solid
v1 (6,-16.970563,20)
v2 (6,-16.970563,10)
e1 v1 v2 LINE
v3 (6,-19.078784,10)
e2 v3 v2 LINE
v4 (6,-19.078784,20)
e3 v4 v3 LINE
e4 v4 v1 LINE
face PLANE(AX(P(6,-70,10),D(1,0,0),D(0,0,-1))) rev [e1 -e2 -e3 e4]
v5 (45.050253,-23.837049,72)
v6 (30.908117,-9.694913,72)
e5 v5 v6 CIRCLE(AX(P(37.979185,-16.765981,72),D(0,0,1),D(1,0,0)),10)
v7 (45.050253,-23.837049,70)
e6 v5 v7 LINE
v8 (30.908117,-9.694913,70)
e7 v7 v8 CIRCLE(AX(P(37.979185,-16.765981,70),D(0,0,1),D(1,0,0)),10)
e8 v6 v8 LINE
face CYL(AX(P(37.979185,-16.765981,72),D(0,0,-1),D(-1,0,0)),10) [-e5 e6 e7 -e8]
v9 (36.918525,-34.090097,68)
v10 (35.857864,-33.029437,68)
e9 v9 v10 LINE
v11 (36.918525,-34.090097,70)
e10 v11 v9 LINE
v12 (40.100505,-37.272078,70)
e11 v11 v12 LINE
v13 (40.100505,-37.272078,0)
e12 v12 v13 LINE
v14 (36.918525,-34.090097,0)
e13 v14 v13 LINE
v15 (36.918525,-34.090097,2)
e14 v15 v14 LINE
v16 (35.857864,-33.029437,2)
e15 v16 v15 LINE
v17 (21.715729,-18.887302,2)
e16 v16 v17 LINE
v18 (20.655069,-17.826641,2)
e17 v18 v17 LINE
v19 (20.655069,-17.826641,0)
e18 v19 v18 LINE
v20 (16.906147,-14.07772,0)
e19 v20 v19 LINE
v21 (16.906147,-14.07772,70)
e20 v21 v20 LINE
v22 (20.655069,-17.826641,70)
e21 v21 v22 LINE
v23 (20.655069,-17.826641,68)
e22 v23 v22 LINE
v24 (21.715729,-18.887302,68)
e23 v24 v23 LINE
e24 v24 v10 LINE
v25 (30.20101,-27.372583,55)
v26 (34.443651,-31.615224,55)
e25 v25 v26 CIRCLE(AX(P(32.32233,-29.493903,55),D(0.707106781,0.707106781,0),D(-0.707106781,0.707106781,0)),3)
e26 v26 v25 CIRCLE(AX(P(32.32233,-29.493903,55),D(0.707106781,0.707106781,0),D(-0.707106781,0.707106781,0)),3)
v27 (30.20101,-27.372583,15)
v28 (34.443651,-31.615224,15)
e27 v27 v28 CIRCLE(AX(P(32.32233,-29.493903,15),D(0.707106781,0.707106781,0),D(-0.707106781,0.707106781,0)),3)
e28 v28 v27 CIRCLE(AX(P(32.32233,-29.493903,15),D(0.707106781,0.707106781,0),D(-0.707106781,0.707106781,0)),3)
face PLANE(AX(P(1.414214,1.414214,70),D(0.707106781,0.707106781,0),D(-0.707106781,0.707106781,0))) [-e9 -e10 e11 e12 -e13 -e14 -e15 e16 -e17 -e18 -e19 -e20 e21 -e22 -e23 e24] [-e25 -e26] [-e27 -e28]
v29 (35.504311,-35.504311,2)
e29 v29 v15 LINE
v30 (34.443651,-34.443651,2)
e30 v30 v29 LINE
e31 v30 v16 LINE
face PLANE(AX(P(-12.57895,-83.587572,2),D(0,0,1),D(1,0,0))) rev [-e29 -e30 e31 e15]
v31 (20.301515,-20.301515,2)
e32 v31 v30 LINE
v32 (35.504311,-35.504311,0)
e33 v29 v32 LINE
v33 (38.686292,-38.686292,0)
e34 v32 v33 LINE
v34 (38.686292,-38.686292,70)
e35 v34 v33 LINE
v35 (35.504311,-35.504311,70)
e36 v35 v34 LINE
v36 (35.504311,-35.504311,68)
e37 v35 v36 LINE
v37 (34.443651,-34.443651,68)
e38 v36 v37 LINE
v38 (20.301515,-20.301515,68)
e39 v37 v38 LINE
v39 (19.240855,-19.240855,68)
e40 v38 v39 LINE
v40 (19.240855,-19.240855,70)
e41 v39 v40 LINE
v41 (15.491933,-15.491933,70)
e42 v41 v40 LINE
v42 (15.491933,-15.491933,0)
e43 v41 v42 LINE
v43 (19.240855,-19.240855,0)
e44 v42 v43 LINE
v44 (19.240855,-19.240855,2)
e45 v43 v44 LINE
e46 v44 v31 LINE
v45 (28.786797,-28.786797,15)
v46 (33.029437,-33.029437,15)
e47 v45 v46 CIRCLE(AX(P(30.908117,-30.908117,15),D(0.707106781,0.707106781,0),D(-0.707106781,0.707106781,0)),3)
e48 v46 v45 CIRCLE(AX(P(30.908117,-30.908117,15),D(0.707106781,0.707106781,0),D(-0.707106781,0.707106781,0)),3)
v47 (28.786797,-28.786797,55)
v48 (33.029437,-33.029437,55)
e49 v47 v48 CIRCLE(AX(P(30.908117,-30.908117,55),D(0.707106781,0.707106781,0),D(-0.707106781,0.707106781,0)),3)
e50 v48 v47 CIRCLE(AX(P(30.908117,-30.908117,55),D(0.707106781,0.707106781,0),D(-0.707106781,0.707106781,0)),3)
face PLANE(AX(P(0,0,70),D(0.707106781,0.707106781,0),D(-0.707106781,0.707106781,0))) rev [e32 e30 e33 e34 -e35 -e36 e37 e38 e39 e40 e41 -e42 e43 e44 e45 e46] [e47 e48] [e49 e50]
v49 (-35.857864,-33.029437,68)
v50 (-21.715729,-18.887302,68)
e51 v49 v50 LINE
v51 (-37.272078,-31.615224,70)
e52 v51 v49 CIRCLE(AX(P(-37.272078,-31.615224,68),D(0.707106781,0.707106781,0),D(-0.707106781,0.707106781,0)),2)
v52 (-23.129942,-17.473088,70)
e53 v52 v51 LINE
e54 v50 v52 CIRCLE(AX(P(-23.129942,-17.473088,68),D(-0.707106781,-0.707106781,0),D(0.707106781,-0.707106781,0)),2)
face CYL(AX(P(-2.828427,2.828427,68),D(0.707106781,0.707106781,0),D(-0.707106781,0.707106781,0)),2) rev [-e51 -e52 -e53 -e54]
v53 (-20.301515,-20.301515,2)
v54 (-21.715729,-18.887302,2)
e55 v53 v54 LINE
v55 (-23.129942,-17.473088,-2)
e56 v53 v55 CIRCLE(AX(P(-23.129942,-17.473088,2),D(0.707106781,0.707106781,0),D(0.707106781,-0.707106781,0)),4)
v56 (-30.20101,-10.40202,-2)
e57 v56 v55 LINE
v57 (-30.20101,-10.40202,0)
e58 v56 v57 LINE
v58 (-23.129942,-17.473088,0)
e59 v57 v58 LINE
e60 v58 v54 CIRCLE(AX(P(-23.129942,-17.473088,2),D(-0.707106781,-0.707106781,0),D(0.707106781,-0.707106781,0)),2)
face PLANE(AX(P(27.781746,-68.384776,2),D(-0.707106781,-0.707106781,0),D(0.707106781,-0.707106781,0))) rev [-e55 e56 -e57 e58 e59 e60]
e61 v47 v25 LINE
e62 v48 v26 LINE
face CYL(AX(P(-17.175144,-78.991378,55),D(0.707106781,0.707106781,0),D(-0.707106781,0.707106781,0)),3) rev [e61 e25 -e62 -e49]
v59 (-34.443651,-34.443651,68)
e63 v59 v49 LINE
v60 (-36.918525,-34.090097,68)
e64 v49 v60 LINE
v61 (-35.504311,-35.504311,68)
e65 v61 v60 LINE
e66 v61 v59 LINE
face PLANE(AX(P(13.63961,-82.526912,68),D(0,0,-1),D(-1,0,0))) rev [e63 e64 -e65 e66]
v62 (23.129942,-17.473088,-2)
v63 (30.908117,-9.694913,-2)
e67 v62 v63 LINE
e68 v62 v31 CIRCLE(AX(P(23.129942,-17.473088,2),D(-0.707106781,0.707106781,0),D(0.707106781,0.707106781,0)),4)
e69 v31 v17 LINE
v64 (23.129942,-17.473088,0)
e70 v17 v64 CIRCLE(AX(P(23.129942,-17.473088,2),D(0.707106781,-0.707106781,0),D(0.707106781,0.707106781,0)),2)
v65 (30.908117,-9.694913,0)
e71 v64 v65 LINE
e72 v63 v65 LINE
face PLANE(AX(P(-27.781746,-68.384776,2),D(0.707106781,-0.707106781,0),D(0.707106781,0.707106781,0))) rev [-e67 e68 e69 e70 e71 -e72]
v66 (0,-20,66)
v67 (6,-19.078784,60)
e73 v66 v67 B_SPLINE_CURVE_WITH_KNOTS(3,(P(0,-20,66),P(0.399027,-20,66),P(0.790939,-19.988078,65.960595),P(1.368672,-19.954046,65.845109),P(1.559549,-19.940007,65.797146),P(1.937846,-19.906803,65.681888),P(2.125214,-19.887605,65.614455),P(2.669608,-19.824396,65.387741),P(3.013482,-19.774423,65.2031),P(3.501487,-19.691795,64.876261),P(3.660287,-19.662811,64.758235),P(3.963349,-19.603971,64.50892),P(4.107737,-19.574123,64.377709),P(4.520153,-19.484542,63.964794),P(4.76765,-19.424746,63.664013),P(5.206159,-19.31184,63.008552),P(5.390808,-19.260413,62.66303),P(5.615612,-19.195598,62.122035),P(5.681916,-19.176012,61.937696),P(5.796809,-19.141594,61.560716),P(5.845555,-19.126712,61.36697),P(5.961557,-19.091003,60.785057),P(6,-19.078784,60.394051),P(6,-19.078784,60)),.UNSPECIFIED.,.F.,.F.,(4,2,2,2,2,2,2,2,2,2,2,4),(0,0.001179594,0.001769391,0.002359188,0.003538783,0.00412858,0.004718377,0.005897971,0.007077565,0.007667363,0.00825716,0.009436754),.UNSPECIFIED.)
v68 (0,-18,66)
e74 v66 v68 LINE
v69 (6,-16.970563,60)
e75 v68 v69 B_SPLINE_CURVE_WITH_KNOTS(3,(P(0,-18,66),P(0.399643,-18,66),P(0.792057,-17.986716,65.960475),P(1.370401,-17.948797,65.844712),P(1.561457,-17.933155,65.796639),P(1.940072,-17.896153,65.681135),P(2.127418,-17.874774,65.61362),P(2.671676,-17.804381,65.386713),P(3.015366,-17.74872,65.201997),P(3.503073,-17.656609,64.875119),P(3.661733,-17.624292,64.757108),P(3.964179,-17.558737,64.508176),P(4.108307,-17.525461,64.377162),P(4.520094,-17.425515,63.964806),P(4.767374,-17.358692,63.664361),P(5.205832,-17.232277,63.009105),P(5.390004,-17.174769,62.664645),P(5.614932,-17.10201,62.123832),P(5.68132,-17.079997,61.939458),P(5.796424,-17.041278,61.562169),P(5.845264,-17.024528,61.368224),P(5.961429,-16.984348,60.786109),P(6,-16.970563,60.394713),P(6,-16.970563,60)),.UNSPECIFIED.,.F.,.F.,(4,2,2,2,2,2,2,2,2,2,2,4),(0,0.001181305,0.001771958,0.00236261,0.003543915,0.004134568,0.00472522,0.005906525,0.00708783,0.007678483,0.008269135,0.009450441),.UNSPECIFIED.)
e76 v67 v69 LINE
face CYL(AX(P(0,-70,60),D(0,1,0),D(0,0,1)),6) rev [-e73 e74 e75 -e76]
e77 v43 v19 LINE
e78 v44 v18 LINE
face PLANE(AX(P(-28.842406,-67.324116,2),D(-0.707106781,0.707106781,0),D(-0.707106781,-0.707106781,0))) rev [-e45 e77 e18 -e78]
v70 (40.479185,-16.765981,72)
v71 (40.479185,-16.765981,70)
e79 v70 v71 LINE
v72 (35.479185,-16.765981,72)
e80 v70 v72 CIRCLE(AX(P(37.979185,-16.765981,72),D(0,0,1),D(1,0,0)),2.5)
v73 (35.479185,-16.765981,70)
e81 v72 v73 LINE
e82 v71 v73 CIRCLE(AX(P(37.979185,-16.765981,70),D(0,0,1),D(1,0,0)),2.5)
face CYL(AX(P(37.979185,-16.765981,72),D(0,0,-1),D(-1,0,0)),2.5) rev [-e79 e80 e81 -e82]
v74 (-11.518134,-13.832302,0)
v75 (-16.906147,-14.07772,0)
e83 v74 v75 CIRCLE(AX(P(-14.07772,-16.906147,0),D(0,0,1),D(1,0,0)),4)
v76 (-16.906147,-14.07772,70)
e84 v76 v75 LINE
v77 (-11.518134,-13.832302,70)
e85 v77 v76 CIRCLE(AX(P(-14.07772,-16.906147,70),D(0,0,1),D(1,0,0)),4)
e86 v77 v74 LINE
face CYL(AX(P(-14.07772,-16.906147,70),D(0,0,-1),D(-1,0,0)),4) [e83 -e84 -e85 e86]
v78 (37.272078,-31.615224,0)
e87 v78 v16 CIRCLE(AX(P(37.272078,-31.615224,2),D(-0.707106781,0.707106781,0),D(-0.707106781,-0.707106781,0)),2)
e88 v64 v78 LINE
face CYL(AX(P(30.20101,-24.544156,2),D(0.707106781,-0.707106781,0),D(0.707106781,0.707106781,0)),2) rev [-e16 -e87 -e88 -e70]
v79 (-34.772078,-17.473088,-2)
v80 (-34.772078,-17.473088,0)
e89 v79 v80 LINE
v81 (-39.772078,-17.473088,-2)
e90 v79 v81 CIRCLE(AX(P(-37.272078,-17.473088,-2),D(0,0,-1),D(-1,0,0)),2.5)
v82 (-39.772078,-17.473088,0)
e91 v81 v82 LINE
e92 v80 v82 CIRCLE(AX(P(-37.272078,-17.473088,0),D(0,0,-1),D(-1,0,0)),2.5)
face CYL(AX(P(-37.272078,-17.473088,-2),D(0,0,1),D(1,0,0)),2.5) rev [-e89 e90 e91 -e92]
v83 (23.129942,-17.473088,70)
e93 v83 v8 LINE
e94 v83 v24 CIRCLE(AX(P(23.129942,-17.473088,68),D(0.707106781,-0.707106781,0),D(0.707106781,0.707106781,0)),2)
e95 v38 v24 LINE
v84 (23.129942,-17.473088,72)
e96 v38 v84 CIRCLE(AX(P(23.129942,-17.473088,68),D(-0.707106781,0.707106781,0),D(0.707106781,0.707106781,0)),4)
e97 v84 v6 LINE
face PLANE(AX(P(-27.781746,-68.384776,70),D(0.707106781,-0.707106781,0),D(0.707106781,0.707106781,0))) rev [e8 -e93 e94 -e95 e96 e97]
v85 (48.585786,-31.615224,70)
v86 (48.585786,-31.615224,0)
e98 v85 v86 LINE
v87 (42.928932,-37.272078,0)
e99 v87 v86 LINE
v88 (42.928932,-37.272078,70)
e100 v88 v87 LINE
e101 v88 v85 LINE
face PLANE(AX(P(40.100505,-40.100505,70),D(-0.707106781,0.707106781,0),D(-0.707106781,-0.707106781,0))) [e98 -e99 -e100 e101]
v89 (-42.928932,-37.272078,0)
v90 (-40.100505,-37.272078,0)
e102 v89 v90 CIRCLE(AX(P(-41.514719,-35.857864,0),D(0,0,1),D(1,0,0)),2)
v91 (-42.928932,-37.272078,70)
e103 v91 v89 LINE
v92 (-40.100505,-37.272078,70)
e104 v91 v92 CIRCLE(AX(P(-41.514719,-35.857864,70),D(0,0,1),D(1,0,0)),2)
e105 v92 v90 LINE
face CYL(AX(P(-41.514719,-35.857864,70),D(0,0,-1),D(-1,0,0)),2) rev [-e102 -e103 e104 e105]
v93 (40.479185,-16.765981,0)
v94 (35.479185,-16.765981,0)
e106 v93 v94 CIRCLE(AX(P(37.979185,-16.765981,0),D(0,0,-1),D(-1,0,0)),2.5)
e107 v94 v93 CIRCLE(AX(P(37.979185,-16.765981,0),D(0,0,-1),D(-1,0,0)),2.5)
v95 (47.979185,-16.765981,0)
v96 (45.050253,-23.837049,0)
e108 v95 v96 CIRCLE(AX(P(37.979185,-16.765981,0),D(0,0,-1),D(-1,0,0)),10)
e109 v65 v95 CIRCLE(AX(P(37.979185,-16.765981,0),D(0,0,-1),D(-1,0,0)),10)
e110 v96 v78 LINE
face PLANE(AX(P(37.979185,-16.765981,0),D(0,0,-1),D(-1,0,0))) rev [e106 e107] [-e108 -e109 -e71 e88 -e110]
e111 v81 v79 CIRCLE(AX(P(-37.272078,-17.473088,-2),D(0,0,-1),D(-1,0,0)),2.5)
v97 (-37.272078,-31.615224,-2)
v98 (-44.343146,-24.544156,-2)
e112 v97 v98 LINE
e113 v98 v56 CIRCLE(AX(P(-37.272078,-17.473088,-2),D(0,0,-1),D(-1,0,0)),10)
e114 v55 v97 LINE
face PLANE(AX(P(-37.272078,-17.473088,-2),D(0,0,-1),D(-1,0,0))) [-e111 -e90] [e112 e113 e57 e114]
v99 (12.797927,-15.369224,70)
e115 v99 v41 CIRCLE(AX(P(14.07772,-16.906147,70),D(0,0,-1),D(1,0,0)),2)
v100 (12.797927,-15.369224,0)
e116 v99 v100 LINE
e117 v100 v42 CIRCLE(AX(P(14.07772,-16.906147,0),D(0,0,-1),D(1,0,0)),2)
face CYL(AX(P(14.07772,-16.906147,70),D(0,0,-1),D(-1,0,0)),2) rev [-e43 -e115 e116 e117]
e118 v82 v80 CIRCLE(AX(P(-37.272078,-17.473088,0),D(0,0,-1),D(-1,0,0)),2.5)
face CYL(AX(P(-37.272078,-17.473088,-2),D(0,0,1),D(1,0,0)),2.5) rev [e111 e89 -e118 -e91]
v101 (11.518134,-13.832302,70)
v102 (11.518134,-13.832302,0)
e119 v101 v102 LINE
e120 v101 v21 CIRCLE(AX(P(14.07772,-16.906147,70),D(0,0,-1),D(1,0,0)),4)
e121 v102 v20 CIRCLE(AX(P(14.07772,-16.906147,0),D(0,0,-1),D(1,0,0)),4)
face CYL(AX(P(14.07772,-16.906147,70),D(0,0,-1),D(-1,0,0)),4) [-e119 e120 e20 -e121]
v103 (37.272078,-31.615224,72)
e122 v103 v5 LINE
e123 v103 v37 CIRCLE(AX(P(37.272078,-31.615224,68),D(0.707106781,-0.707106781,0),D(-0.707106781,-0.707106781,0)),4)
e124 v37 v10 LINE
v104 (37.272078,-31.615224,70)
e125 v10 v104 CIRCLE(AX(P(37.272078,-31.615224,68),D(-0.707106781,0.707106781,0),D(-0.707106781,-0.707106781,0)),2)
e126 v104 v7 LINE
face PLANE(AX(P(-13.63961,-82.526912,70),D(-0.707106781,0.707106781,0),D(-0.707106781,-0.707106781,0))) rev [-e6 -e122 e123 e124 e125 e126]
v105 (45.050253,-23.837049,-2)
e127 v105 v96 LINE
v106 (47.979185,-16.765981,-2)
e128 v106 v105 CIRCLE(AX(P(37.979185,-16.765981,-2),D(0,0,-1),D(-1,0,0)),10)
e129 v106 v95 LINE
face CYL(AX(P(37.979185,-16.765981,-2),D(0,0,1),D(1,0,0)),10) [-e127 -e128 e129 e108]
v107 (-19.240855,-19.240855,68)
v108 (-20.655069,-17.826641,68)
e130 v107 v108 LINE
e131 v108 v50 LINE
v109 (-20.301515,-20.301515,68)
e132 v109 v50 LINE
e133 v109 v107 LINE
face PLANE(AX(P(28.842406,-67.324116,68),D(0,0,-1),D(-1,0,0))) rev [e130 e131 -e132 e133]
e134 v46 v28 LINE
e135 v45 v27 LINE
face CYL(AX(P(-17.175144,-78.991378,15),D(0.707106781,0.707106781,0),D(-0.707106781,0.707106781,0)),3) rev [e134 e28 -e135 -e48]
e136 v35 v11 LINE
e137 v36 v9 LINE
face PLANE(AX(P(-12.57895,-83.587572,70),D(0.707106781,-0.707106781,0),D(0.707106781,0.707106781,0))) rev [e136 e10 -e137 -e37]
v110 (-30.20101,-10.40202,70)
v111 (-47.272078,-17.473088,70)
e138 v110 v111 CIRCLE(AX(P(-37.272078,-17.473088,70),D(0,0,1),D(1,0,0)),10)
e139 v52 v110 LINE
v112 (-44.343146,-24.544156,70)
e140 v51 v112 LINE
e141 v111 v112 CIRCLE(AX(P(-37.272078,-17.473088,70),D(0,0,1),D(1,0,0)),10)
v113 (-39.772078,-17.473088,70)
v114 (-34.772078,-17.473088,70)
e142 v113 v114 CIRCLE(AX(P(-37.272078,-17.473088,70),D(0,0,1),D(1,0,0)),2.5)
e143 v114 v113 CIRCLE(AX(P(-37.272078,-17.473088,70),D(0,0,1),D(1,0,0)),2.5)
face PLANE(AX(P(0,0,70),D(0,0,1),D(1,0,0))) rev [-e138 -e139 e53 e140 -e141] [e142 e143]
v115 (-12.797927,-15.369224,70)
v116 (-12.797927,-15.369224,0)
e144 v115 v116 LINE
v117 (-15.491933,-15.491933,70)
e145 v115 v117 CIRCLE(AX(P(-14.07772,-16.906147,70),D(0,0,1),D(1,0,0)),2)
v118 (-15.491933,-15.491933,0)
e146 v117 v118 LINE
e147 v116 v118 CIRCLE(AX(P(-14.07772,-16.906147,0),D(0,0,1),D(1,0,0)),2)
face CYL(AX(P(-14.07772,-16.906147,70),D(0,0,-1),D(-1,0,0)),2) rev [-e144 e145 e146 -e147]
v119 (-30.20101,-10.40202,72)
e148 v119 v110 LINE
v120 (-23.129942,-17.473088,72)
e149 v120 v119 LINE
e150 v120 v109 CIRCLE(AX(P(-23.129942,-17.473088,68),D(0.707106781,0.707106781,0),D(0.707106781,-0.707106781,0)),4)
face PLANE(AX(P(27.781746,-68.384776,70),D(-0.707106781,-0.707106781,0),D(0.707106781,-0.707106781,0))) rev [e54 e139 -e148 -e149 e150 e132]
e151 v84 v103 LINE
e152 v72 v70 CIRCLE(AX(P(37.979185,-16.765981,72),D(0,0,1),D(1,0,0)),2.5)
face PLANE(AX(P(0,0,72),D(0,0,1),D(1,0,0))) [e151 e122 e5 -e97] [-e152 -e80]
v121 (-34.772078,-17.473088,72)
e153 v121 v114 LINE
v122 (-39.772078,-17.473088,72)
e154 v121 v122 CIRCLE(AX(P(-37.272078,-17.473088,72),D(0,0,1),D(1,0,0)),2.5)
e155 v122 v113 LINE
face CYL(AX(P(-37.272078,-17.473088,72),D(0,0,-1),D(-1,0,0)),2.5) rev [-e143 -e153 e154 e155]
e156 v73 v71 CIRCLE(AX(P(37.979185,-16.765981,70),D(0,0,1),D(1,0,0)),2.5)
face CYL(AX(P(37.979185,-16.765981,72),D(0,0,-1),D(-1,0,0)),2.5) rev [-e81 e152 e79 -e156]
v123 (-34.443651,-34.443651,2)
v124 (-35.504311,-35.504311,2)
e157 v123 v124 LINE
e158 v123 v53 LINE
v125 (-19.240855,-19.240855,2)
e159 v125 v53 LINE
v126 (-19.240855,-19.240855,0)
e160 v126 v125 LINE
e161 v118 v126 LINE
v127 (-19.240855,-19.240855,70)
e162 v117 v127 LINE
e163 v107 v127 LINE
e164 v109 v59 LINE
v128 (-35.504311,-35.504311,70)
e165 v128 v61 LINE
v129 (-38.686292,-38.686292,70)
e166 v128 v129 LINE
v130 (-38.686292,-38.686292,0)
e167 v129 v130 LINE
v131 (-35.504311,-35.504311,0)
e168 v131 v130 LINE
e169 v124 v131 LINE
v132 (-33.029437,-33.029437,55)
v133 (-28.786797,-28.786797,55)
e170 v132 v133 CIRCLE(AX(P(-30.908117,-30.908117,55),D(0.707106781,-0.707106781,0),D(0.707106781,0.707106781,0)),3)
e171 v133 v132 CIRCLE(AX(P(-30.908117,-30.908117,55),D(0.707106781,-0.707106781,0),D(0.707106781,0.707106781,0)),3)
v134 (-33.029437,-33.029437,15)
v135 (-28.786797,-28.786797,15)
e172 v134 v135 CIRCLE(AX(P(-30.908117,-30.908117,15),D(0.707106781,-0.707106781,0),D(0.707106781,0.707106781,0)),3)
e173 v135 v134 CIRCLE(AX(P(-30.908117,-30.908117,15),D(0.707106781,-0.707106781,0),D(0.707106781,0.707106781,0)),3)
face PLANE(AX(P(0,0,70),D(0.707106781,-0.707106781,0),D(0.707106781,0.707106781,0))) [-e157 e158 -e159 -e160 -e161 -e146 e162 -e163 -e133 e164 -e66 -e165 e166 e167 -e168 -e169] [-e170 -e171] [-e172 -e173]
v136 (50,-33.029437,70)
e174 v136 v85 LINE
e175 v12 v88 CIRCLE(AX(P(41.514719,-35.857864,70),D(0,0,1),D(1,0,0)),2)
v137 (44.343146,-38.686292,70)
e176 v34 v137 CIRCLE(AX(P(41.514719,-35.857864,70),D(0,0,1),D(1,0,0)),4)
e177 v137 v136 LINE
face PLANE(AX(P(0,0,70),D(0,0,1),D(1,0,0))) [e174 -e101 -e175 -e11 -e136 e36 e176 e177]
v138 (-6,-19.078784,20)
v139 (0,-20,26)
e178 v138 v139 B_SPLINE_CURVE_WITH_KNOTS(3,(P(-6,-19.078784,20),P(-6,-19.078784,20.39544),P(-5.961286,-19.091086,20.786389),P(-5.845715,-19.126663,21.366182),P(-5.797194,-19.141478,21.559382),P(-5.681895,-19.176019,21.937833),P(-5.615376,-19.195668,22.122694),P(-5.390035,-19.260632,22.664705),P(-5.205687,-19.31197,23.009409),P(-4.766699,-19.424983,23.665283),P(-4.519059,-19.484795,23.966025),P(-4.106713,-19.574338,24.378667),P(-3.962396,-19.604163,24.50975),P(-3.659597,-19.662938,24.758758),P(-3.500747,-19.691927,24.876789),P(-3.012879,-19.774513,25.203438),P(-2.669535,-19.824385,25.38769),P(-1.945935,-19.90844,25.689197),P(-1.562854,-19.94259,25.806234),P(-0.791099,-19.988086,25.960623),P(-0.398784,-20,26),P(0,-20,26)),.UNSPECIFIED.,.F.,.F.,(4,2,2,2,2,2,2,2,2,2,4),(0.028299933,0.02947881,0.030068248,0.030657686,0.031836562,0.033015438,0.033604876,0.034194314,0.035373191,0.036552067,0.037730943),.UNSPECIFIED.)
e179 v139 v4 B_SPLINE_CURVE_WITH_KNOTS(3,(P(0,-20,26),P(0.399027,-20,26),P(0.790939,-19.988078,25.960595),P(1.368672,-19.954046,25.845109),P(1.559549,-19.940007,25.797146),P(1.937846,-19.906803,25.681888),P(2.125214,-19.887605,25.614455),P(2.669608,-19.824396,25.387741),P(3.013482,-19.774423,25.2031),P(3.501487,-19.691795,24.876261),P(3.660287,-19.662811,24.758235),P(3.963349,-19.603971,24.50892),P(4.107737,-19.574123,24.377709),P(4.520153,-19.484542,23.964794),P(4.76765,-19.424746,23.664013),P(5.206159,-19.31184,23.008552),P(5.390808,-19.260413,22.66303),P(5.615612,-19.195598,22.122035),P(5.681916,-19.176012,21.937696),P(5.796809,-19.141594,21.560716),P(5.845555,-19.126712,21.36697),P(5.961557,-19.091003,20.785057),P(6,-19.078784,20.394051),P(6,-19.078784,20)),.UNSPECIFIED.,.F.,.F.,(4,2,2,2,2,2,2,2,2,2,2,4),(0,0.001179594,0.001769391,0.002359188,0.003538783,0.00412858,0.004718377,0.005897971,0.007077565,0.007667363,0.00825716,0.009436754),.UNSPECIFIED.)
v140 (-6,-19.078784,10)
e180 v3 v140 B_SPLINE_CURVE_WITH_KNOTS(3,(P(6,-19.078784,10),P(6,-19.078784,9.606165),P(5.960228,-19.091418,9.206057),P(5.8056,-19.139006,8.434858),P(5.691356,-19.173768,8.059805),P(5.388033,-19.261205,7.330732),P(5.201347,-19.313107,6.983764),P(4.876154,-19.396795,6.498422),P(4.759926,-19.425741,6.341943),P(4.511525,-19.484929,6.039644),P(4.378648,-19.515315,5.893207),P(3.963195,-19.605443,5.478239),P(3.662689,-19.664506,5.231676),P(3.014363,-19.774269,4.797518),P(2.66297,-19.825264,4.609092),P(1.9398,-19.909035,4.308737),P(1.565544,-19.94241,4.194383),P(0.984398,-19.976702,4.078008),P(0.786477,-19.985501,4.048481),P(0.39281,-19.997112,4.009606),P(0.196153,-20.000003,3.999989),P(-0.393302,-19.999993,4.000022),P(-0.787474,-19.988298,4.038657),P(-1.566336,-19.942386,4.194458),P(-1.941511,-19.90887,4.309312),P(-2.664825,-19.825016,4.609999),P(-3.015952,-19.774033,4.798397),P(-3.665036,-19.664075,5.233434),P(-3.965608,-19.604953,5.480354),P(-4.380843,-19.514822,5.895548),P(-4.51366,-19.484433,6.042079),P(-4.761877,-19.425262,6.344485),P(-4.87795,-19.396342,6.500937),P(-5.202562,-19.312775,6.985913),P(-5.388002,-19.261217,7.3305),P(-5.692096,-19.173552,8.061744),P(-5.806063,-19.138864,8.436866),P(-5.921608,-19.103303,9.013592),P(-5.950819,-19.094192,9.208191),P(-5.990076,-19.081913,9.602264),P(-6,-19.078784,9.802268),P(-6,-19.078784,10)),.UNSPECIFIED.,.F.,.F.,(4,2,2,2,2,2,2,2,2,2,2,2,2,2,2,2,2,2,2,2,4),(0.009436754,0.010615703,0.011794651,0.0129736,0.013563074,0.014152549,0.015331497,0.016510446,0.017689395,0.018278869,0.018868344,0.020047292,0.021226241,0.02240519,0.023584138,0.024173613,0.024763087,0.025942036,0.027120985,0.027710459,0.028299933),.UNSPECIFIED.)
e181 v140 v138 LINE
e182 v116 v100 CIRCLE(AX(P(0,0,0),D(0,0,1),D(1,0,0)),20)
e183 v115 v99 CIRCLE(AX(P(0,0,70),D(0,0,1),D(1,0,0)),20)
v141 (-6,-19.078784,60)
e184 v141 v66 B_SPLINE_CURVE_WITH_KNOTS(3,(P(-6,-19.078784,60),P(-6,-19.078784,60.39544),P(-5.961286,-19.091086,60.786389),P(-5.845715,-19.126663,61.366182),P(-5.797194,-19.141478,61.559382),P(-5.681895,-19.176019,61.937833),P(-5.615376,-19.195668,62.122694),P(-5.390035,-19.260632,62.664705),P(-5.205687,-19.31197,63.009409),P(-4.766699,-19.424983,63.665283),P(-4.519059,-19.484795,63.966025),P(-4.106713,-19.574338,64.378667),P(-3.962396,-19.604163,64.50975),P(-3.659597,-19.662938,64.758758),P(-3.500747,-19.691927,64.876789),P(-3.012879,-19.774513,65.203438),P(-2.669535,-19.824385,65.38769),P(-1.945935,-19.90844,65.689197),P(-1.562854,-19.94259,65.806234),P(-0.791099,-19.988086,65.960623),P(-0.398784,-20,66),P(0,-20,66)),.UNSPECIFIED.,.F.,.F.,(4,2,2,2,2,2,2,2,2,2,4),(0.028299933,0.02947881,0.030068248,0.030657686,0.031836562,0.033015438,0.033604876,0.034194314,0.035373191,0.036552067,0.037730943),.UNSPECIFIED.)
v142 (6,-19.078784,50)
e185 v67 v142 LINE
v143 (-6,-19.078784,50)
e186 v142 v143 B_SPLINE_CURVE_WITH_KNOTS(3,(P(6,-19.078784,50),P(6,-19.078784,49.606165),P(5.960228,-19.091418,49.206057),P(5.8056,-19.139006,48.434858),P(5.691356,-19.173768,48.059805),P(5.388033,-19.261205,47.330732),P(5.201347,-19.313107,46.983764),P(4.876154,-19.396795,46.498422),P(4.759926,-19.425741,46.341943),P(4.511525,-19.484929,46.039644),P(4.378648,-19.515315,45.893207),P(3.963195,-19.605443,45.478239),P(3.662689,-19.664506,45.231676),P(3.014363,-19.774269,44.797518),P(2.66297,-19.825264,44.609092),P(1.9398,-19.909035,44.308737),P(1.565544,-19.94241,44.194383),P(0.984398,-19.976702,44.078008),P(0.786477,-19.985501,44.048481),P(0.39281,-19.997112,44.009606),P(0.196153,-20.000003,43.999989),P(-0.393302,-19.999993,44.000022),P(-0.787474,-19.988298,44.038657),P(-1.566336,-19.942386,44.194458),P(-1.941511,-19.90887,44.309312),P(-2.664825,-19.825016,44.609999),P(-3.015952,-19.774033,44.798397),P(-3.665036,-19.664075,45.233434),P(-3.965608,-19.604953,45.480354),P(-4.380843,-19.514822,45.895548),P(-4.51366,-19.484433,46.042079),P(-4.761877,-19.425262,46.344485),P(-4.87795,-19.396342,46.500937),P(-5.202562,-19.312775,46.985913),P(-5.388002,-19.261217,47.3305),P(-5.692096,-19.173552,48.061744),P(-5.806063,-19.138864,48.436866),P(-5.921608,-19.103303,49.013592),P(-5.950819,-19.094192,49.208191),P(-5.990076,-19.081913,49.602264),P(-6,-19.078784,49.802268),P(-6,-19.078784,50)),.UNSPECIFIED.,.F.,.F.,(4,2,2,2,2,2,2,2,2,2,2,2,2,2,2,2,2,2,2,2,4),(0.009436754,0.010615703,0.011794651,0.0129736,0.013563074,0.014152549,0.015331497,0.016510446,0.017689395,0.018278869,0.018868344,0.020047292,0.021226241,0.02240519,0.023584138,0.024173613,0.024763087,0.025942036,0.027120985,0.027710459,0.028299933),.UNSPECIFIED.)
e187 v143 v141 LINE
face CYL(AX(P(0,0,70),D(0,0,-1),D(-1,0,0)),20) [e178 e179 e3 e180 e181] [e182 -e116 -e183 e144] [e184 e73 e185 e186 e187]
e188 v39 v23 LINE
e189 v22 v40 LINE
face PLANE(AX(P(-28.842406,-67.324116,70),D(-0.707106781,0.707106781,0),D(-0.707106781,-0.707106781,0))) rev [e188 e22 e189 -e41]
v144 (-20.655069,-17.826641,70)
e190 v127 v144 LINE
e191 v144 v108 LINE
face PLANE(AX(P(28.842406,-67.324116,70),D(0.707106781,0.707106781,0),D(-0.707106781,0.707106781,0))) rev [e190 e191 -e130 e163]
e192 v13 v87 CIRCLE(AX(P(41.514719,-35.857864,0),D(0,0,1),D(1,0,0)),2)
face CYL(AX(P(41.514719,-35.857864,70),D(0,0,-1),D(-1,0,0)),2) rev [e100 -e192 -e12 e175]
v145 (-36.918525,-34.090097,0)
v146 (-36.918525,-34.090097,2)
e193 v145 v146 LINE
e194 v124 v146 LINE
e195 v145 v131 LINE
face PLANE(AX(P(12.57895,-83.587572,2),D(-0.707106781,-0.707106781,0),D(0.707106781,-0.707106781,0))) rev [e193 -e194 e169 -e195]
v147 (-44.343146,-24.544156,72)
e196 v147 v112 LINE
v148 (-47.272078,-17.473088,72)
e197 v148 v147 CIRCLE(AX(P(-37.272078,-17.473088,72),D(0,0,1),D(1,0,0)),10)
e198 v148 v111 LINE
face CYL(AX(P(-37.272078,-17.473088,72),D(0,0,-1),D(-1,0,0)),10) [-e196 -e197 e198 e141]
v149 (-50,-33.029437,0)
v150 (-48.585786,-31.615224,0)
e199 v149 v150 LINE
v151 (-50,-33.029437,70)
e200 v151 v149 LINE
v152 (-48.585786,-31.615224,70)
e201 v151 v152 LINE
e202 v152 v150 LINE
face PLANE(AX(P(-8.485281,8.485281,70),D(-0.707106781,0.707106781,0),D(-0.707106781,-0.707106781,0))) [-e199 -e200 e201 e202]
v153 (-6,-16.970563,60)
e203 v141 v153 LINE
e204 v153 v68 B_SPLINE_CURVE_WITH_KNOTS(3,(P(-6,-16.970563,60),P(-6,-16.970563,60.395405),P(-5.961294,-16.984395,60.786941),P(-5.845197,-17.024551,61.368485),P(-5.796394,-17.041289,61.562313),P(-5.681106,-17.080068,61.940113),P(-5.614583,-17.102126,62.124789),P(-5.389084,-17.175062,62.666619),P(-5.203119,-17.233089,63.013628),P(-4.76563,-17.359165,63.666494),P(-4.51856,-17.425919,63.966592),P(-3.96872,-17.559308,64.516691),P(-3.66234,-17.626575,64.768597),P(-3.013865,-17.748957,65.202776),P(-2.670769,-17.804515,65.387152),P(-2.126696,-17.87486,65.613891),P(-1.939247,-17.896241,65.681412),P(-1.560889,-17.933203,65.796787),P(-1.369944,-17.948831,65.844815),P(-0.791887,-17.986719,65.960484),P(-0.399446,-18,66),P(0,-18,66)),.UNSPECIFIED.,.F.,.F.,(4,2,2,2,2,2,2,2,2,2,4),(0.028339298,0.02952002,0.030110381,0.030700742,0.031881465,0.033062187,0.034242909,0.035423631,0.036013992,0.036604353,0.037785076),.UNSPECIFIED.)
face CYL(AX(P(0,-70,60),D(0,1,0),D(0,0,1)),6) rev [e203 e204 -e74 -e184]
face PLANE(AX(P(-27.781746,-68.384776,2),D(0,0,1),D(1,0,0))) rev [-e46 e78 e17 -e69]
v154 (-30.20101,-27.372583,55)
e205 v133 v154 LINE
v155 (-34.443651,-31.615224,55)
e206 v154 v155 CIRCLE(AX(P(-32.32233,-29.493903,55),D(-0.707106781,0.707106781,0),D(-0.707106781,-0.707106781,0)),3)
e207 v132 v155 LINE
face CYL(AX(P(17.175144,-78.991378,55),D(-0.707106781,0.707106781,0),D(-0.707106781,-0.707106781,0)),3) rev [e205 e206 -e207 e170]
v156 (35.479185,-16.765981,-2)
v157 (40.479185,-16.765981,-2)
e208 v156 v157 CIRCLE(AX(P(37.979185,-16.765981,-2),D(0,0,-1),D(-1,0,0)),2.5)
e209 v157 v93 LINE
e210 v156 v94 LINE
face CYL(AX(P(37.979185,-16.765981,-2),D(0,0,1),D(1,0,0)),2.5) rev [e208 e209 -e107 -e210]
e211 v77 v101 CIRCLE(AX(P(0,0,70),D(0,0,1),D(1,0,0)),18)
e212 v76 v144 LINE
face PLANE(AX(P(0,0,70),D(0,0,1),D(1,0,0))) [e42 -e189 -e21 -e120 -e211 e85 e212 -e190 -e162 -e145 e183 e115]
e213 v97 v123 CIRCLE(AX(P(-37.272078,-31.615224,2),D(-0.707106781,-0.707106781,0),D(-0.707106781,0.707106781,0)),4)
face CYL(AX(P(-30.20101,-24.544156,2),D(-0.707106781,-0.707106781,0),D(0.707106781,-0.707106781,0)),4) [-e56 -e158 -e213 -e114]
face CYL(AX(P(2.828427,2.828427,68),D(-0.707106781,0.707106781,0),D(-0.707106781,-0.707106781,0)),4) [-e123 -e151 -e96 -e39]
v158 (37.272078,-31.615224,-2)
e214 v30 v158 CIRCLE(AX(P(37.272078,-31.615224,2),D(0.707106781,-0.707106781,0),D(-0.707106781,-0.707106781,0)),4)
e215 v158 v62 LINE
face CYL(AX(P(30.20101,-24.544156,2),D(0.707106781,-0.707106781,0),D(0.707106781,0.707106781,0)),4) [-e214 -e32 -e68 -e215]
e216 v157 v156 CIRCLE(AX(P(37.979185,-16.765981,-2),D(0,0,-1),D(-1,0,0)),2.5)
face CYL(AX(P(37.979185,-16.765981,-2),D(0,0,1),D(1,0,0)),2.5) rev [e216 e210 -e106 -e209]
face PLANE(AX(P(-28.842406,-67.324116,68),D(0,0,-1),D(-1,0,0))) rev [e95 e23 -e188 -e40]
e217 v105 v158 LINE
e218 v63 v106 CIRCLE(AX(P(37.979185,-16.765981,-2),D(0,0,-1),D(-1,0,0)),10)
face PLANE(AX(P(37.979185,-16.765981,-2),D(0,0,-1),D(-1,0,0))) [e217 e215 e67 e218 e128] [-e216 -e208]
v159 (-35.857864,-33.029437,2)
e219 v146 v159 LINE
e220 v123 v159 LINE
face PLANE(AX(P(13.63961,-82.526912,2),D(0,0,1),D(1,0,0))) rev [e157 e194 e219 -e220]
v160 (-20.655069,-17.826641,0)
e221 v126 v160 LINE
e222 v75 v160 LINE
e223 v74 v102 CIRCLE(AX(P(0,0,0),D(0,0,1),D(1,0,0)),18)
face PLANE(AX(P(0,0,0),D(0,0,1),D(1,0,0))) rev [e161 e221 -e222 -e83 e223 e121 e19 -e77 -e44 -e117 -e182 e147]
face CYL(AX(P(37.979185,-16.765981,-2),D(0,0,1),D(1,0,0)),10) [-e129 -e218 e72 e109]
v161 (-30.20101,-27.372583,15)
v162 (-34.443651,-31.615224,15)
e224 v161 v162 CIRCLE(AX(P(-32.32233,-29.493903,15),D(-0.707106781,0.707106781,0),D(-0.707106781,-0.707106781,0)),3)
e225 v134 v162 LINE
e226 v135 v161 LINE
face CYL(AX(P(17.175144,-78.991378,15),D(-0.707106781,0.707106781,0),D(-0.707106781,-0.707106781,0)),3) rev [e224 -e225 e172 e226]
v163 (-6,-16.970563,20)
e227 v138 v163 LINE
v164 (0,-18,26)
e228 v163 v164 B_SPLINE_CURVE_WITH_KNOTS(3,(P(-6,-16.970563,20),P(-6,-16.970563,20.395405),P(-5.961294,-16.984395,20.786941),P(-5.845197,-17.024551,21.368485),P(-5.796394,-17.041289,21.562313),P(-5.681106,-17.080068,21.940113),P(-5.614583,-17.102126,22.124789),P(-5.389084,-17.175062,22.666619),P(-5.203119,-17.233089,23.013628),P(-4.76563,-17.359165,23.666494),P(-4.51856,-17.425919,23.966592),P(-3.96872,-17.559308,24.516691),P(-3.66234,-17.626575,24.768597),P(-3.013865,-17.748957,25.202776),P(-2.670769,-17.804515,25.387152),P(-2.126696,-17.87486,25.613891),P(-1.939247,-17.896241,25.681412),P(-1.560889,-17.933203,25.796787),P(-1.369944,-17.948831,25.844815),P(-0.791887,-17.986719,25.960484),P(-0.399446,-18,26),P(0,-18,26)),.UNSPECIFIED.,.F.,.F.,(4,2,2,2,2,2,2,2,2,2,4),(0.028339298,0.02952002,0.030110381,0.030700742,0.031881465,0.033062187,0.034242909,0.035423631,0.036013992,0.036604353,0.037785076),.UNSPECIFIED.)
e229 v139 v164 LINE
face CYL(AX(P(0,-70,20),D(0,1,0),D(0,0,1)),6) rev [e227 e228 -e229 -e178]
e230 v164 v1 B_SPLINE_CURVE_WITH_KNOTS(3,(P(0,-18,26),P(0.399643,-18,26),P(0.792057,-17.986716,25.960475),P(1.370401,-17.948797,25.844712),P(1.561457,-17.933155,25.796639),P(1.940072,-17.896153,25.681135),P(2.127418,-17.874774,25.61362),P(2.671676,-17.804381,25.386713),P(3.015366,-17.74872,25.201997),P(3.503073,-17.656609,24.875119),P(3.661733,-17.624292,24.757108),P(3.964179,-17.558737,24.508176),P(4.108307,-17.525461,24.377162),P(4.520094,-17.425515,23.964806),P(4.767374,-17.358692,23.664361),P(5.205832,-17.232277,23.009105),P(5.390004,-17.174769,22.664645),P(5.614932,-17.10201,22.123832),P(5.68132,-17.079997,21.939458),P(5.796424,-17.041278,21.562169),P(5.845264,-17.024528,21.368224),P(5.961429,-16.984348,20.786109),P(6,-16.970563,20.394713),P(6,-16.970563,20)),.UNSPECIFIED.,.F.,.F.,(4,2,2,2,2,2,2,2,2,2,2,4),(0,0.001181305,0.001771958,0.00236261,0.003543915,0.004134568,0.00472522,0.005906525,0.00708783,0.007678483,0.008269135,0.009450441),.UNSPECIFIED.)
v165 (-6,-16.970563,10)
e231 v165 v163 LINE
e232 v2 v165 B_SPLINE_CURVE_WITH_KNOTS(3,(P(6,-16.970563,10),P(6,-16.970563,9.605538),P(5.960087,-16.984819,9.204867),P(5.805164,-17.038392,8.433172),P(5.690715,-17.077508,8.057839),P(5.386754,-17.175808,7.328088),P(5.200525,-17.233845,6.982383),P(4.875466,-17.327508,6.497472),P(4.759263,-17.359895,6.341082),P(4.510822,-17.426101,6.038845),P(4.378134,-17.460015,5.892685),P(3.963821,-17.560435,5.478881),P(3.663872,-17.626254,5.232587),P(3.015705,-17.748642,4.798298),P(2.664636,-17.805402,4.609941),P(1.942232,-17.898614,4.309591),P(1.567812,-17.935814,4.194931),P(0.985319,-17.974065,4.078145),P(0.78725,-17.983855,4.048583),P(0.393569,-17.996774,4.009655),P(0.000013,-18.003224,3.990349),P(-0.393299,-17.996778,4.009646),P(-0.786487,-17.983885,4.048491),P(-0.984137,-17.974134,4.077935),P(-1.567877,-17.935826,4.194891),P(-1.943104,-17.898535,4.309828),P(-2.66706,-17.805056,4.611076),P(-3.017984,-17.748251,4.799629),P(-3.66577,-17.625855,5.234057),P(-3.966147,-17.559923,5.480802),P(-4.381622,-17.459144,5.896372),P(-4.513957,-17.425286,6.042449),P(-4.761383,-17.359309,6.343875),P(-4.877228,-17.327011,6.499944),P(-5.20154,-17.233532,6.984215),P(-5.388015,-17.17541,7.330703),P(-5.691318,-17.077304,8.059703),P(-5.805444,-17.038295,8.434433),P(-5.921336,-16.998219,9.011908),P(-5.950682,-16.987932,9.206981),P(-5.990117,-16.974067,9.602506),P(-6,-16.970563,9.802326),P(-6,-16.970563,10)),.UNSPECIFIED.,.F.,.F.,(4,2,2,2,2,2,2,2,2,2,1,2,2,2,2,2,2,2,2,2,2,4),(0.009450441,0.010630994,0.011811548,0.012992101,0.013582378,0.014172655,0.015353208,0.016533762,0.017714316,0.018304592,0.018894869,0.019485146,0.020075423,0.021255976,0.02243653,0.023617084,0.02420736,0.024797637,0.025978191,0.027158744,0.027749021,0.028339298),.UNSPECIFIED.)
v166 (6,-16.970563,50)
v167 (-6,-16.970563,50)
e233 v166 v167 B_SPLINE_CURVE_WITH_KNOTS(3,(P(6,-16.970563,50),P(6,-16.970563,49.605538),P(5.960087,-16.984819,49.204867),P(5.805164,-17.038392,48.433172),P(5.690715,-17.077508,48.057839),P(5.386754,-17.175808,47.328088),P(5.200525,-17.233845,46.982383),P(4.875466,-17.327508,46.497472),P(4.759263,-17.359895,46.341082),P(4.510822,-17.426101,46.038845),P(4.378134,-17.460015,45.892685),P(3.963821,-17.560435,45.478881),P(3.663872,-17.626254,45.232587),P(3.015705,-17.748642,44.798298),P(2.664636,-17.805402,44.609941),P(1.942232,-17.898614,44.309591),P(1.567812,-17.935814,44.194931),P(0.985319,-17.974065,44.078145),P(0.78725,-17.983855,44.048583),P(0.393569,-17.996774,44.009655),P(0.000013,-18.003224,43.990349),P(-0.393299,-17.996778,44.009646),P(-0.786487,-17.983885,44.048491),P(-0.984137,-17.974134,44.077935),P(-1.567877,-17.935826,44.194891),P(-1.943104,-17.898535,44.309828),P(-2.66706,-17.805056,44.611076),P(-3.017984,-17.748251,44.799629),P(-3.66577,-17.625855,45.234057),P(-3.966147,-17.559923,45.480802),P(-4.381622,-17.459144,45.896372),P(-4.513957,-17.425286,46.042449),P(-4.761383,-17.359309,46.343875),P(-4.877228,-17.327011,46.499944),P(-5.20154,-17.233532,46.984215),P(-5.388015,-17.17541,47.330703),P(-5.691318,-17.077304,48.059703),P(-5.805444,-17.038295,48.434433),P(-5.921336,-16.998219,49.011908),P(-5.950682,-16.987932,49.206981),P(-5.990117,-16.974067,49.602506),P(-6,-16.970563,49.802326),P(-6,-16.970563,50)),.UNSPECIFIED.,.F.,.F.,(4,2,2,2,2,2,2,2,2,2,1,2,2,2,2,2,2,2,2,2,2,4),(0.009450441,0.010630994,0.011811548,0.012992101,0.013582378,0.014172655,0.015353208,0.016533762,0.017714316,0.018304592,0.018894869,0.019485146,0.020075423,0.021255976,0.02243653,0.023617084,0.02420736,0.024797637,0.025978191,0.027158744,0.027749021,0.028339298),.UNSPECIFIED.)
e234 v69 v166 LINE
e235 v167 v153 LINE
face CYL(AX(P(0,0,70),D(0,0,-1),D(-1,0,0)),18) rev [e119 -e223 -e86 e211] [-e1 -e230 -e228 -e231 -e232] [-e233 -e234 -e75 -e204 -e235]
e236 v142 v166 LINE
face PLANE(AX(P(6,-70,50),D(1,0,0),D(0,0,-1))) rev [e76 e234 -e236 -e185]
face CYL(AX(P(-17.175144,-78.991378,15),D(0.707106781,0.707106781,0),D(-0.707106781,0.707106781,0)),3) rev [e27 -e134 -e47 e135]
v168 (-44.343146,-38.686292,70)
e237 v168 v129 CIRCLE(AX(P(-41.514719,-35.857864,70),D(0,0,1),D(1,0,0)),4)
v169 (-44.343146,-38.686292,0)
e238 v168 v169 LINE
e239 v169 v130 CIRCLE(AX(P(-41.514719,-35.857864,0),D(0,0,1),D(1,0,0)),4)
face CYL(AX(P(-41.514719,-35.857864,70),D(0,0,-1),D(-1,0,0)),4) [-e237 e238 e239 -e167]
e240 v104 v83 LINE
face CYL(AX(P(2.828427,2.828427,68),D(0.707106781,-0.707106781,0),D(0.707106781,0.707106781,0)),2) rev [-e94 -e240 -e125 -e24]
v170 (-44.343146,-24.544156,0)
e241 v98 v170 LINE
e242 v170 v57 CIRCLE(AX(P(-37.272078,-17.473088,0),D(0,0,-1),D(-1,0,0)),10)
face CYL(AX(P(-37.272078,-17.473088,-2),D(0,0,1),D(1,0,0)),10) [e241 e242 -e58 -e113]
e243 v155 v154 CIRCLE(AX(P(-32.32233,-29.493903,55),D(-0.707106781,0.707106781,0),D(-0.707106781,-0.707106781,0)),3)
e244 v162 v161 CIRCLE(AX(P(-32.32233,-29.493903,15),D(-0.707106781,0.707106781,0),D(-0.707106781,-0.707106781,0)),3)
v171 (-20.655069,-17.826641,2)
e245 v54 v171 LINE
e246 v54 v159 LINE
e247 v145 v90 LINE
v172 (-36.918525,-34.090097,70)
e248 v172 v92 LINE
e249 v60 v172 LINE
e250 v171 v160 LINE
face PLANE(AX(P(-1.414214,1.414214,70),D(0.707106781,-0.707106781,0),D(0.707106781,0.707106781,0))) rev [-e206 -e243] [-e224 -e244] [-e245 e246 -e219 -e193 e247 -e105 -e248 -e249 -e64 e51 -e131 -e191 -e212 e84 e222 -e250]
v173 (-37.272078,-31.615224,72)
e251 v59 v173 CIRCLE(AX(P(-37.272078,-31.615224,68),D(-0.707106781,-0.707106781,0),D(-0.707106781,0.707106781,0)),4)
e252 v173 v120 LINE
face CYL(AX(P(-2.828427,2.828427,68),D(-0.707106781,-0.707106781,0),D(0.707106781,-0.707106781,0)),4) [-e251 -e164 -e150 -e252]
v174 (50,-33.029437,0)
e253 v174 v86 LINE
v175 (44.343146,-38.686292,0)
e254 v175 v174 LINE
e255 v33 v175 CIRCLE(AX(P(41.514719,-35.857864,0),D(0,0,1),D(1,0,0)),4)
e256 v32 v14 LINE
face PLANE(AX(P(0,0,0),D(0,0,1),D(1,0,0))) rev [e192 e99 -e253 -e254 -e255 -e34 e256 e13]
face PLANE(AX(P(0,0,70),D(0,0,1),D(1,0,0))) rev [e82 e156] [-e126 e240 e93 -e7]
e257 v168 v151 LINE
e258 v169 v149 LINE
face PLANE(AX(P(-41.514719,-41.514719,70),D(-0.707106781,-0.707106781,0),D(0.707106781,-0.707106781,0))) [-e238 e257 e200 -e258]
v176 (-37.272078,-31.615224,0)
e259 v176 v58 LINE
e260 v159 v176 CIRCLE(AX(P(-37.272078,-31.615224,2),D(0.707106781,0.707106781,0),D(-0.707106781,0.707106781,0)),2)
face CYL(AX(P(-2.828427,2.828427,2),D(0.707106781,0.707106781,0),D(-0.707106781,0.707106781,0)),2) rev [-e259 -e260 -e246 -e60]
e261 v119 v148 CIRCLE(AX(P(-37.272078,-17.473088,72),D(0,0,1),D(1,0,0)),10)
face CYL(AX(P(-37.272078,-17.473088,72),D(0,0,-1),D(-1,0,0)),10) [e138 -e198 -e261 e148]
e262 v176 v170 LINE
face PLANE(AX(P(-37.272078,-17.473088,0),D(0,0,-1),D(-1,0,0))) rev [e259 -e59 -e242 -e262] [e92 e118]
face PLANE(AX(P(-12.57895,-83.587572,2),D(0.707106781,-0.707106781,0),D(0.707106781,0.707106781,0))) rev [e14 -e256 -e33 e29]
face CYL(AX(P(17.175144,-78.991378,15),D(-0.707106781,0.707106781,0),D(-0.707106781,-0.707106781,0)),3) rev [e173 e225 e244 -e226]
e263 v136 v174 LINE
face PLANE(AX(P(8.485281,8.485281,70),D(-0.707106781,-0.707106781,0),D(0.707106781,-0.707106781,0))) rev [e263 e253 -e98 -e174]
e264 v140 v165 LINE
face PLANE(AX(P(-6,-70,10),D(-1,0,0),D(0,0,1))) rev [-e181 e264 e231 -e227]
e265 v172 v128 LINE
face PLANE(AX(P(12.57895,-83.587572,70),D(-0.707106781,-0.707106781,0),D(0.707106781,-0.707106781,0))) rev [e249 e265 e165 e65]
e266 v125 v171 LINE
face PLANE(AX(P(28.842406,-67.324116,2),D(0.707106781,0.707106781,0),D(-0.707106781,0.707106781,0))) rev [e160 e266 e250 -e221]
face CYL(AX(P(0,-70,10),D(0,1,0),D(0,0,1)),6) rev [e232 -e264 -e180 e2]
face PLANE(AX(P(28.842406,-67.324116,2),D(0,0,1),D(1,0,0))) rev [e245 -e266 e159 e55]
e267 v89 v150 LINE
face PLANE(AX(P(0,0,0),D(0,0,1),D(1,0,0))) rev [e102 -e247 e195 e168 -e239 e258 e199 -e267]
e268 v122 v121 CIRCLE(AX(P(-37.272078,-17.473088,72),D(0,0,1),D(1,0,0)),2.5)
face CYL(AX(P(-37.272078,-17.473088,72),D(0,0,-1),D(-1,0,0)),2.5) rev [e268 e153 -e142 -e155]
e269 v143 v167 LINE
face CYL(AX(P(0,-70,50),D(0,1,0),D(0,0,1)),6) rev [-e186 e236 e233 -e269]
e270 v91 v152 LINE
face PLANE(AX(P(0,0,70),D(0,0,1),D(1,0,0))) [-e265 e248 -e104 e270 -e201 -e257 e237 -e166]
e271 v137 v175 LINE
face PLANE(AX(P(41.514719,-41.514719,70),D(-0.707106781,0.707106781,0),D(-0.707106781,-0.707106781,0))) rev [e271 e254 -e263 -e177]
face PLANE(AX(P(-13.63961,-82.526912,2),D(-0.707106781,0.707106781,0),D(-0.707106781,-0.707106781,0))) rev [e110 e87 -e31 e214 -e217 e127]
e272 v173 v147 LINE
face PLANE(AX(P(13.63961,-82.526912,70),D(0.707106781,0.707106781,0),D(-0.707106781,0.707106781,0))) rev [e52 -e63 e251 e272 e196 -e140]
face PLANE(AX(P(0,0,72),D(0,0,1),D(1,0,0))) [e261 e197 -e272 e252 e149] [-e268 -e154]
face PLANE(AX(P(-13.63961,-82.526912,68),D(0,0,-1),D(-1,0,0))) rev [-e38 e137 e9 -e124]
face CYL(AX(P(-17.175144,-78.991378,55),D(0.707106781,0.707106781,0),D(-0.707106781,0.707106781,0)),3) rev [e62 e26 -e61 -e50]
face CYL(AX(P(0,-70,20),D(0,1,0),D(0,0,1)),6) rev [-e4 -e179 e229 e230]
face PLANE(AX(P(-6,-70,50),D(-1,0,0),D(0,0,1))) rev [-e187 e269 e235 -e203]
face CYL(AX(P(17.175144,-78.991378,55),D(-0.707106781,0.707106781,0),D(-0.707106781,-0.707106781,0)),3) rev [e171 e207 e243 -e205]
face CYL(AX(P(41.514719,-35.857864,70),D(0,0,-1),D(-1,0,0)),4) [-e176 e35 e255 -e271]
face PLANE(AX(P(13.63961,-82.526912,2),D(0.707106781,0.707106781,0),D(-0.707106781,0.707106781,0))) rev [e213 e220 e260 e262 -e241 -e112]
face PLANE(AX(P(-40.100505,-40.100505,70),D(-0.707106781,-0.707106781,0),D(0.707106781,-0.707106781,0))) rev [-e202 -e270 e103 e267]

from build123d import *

# Parameters (mm, degrees)
SADDLE_BODY_70MM_DEPTH     = 70
FLANGE_NOTCHES_DEPTH       = 70
FLANGE_HOLES_A_SKETCH_R    = 3.0000000000000018
FLANGE_HOLES_A_SKETCH_R_2  = 3
FLANGE_HOLES_A_6_DEPTH     = 70
FLANGE_HOLES_B_SKETCH_R    = 3.0000000000000018
FLANGE_HOLES_B_6_DEPTH     = 70
SADDLE_SLOT_A_SKETCH_W     = 2
SADDLE_SLOT_A_SKETCH_H     = 1.5
SADDLE_SLOT_A_DEPTH        = 70
SADDLE_SLOT_B_SKETCH_W     = 2
SADDLE_SLOT_B_SKETCH_H     = 1.5
SADDLE_SLOT_B_DEPTH        = 70
MOUNTING_EARS_A_SKETCH_R   = 10.000000000000002
MOUNTING_EARS_A_SKETCH_R_2 = 2.5000000000000027
MOUNTING_EARS_A_SKETCH_R_3 = 9.999999999999508
MOUNTING_EARS_A_DEPTH      = 2
MOUNTING_START             = 2
MOUNTING_EARS_B_SKETCH_R   = 2.5000000000000027
MOUNTING_EARS_B_DEPTH      = 2
EAR_FILLETS_R4_R           = 4
EAR_ROOT_FILLETS_R2_R      = 2


with BuildPart() as part:
    # Saddle Profile Sketch → Saddle Body 70mm (new body)
    with BuildSketch(Plane.XY):
        with BuildLine():
            ThreePointArc((-42.928932188134524, -37.27207793864201), (-41.51471862576144, -37.85786437626892), (-40.100505063388304, -37.27207793864207))
            Line((-40.100505063388304, -37.27207793864207), (-16.906146947202778, -14.077719822456547))
            ThreePointArc((-16.906146947202778, -14.077719822456547), (-14.259726515433778, -12.910289897243185), (-11.518134400191764, -13.832302047711334))
            ThreePointArc((-11.518134400191764, -13.832302047711334), (1.1e-15, -18), (11.51813440019177, -13.832302047711329))
            ThreePointArc((11.51813440019177, -13.832302047711329), (14.259726515433789, -12.910289897243175), (16.90614694720279, -14.077719822456542))
            Line((16.90614694720279, -14.077719822456542), (40.10050506338834, -37.27207793864201))
            ThreePointArc((40.10050506338834, -37.27207793864201), (41.51471862576144, -37.857864376268914), (42.92893218813454, -37.272077938642))
            Line((42.92893218813454, -37.272077938642), (48.585786437626965, -31.615223689149577))
            Line((48.585786437626965, -31.615223689149577), (50.00000000000004, -33.029437251522666))
            Line((50.00000000000004, -33.029437251522666), (44.34314575050763, -38.6862915010151))
            ThreePointArc((44.34314575050763, -38.6862915010151), (41.514718625761446, -39.857864376268886), (38.686291501015276, -38.68629150101508))
            Line((38.686291501015276, -38.68629150101508), (15.491933384829723, -15.491933384829608))
            ThreePointArc((15.491933384829723, -15.491933384829608), (14.168723168945196, -14.908218422222957), (12.797927111324189, -15.369224497457033))
            ThreePointArc((12.797927111324189, -15.369224497457033), (5.67e-15, -20), (-12.797927111324178, -15.36922449745704))
            ThreePointArc((-12.797927111324178, -15.36922449745704), (-14.168723168945185, -14.90821842222296), (-15.491933384829686, -15.491933384829643))
            Line((-15.491933384829686, -15.491933384829643), (-38.68629150101524, -38.68629150101511))
            ThreePointArc((-38.68629150101524, -38.68629150101511), (-41.51471862576143, -39.85786437626892), (-44.343145750507624, -38.686291501015106))
            Line((-44.343145750507624, -38.686291501015106), (-49.999999999999986, -33.02943725152272))
            Line((-49.999999999999986, -33.02943725152272), (-48.58578643762691, -31.61522368914963))
            Line((-48.58578643762691, -31.61522368914963), (-42.928932188134524, -37.27207793864201))
        make_face()
    extrude(amount=SADDLE_BODY_70MM_DEPTH)

    # Flange Notches Sketch → Flange Notches (cut)
    with BuildSketch(Plane(origin=(0, 0, 0), x_dir=(1, 0, 0), z_dir=(0, 1, 0))):
        with BuildLine():
            Line((-6.000000000000002, -10), (-6.000000000000002, -19.999999999999996))
            ThreePointArc((-6.000000000000002, -19.999999999999996), (-1.71e-15, -26), (6, -19.999999999999996))
            Line((6, -19.999999999999996), (6, -10))
            ThreePointArc((6, -10), (-4.3e-16, -3.999999999999999), (-6.000000000000002, -10))
        make_face()
        with BuildLine():
            Line((-6.000000000000001, -50), (-5.999999999999999, -60.00000000000001))
            ThreePointArc((-5.999999999999999, -60.00000000000001), (-1.97e-15, -66), (5.999999999999997, -60.00000000000001))
            Line((5.999999999999997, -60.00000000000001), (5.999999999999999, -50))
            ThreePointArc((5.999999999999999, -50), (-5e-16, -44), (-6.000000000000001, -50))
        make_face()
    extrude(amount=-FLANGE_NOTCHES_DEPTH, mode=Mode.SUBTRACT)

    # Flange Holes A Sketch → Flange Holes A Ø6 (cut)
    with BuildSketch(Plane(origin=(1.4142135623730954, 1.4142135623731005, 0), x_dir=(0, 0, -1), z_dir=(0.7071067811865465, 0.7071067811865487, 0))):
        with Locations(Location((-55.00000000000001, -43.710678118654656, 0), (0, 0, 90))):
            Circle(FLANGE_HOLES_A_SKETCH_R)
        with Locations(Location((-15, -43.710678118654656, 0), (0, 0, 90))):
            Circle(FLANGE_HOLES_A_SKETCH_R_2)
    extrude(amount=-FLANGE_HOLES_A_6_DEPTH, mode=Mode.SUBTRACT)

    # Flange Holes B Sketch → Flange Holes B Ø6 (cut)
    with BuildSketch(Plane(origin=(-1.414213562373113, 1.4142135623731131, 0), x_dir=(0, 0, 1), z_dir=(-0.7071067811865476, 0.7071067811865476, 0))):
        with Locations(Location((15, -43.710678118654634, 0), (0, 0, 270))):
            Circle(FLANGE_HOLES_B_SKETCH_R)
        with Locations(Location((55.00000000000001, -43.710678118654634, 0), (0, 0, 270))):
            Circle(FLANGE_HOLES_B_SKETCH_R)
    extrude(amount=-FLANGE_HOLES_B_6_DEPTH, mode=Mode.SUBTRACT)

    # Saddle Slot A Sketch → Saddle Slot A (cut)
    with BuildSketch(Plane(origin=(-1.414213562373113, 1.4142135623731131, 0), x_dir=(0, 0, 1), z_dir=(-0.7071067811865476, 0.7071067811865476, 0))):
        with Locations((69, -27.96067811865464)):
            Rectangle(SADDLE_SLOT_A_SKETCH_W, SADDLE_SLOT_A_SKETCH_H)
        with Locations((69, -49.460678118654634)):
            Rectangle(SADDLE_SLOT_A_SKETCH_W, SADDLE_SLOT_A_SKETCH_H)
        Polygon((2.000000000000001, -27.210678118654652), (2.000000000000001, -28.710678118654638), (0, -28.710678118654638), (-2.8e-16, -27.210678118654652), align=None)
        Polygon((1.9999999999999913, -48.71067811865465), (1.999999999999994, -50.21067811865465), (2.8e-16, -50.21067811865465), (3.67e-15, -48.71067811865465), align=None)
    extrude(amount=-SADDLE_SLOT_A_DEPTH, mode=Mode.SUBTRACT)

    # Saddle Slot B Sketch → Saddle Slot B (cut)
    with BuildSketch(Plane(origin=(1.4142135623730954, 1.4142135623731005, 0), x_dir=(0, 0, -1), z_dir=(0.7071067811865465, 0.7071067811865487, 0))):
        with Locations((-69, -49.46067811865466)):
            Rectangle(SADDLE_SLOT_B_SKETCH_W, SADDLE_SLOT_B_SKETCH_H)
        with Locations((-69, -27.96067811865466)):
            Rectangle(SADDLE_SLOT_B_SKETCH_W, SADDLE_SLOT_B_SKETCH_H)
        Polygon((-2.000000000000001, -50.210678118654656), (-2.000000000000001, -48.71067811865466), (0, -48.71067811865466), (9e-17, -50.210678118654656), align=None)
        Polygon((-2.0000000000000013, -28.71067811865466), (0, -28.71067811865466), (0, -27.21067811865466), (-2.000000000000001, -27.21067811865466), align=None)
    extrude(amount=-SADDLE_SLOT_B_DEPTH, mode=Mode.SUBTRACT)

    # Mounting Ears A Sketch → Mounting Ears A (add)
    # profile 1 of 5: a face of its own
    with BuildSketch(Plane.XY.offset(70)):
        with Locations((-37.272077938642106, -17.473088065418725)):
            Circle(MOUNTING_EARS_A_SKETCH_R)
        with Locations((-37.272077938642106, -17.473088065418725)):
            Circle(MOUNTING_EARS_A_SKETCH_R_2, mode=Mode.SUBTRACT)
    # profile 2 of 5: a face of its own
    with BuildSketch(Plane.XY.offset(70)):
        with BuildLine():
            Line((-34.44365081389593, -34.44365081389581), (-20.301515190164952, -20.30151519016488))
            Line((-20.301515190164952, -20.30151519016488), (-30.20101012677664, -10.402020253553237))
            ThreePointArc((-30.20101012677664, -10.402020253553237), (-28.033282613529238, -13.646253741767818), (-27.272077938642106, -17.473088065418725))
            ThreePointArc((-27.272077938642106, -17.47308806541873), (-33.445243614991206, -26.711883390531593), (-44.343145750507574, -24.54415587728421))
            Line((-44.34314575050757, -24.544155877284215), (-34.44365081389593, -34.44365081389581))
        make_face()
    # profile 3 of 5: a face of its own
    with BuildSketch(Plane.XY.offset(70)):
        with BuildLine():
            Line((21.715728752538062, -18.887301627791807), (35.85786437626904, -33.02943725152273))
            Line((35.85786437626899, -33.02943725152268), (45.05025253169403, -23.83704909609701))
            ThreePointArc((45.05025253169403, -23.837049096097015), (30.908116907963546, -23.83704909609726), (30.908116907963763, -9.694913472366775))
            Line((30.908116907963763, -9.694913472366776), (21.71572875253811, -18.88730162779185))
        make_face()
    # profile 4 of 5: a face of its own
    with BuildSketch(Plane.XY.offset(70)):
        with Locations((37.979184719828666, -16.765981284232126)):
            Circle(MOUNTING_EARS_A_SKETCH_R_3)
        with Locations((37.979184719828666, -16.765981284232126)):
            Circle(MOUNTING_EARS_A_SKETCH_R_2, mode=Mode.SUBTRACT)
    # profile 5 of 5: a face of its own
    with BuildSketch(Plane.XY.offset(70)):
        Polygon((35.85786437626904, -33.02943725152273), (21.715728752538062, -18.887301627791803), (20.30151519016497, -20.301515190164896), (34.44365081389596, -34.443650813895815), align=None)
    extrude(amount=MOUNTING_EARS_A_DEPTH)

    # Mounting Ears B Sketch → Mounting Ears B (add)
    # profile 1 of 2: a face of its own
    with BuildSketch(Plane(origin=(0, 0, 0), x_dir=(-1, 0, 0), z_dir=(0, 0, -1)).offset(MOUNTING_START)):
        with BuildLine():
            Line((-30.90811690796376, -9.694913472366778), (-20.30151519016498, -20.30151519016489))
            Line((-20.30151519016498, -20.30151519016489), (-34.44365081389596, -34.443650813895815))
            Line((-34.44365081389596, -34.443650813895815), (-45.050252531694035, -23.83704909609701))
            ThreePointArc((-45.050252531694035, -23.83704909609701), (-45.050252531693786, -9.694913472366988), (-30.90811690796376, -9.694913472366778))
        make_face()
        with Locations(Location((-37.979184719828666, -16.765981284232126, 0), (0, 0, 180))):
            Circle(MOUNTING_EARS_B_SKETCH_R, mode=Mode.SUBTRACT)
    # profile 2 of 2: a face of its own
    with BuildSketch(Plane(origin=(0, 0, 0), x_dir=(-1, 0, 0), z_dir=(0, 0, -1)).offset(MOUNTING_START)):
        with BuildLine():
            Line((30.201010126776644, -10.402020253553237), (20.301515190164952, -20.30151519016488))
            Line((20.301515190164952, -20.30151519016488), (34.44365081389595, -34.443650813895815))
            Line((34.44365081389595, -34.443650813895815), (44.34314575050756, -24.54415587728423))
            ThreePointArc((44.34314575050756, -24.54415587728423), (44.3431457505076, -10.402020253553266), (30.201010126776644, -10.402020253553237))
        make_face()
        with Locations(Location((37.272077938642106, -17.473088065418725, 0), (0, 0, 180))):
            Circle(MOUNTING_EARS_B_SKETCH_R, mode=Mode.SUBTRACT)
    extrude(amount=-MOUNTING_EARS_B_DEPTH)

    # Ear Fillets R4
    ear_fillets_r4_edges = [part.edges().sort_by_distance(p)[0] for p in [
        (27.372583002030467, -27.372583002030353, -2),
        (27.372583002030463, -27.372583002030353, 72),
        (-27.37258300203044, -27.372583002030346, 72),
        (-27.372583002030453, -27.372583002030346, -2),
    ]]
    fillet(ear_fillets_r4_edges, radius=EAR_FILLETS_R4_R)

    # Ear Root Fillets R2
    ear_root_fillets_r2_edges = [part.edges().sort_by_distance(p)[0] for p in [
        (28.786796564403556, -25.958369439657268, 70),
        (-28.786796564403513, -25.958369439657282, 70),
        (28.786796564403556, -25.958369439657268, 0),
        (-28.786796564403524, -25.95836943965729, 0),
    ]]
    fillet(ear_root_fillets_r2_edges, radius=EAR_ROOT_FILLETS_R2_R)


solid = part.part
